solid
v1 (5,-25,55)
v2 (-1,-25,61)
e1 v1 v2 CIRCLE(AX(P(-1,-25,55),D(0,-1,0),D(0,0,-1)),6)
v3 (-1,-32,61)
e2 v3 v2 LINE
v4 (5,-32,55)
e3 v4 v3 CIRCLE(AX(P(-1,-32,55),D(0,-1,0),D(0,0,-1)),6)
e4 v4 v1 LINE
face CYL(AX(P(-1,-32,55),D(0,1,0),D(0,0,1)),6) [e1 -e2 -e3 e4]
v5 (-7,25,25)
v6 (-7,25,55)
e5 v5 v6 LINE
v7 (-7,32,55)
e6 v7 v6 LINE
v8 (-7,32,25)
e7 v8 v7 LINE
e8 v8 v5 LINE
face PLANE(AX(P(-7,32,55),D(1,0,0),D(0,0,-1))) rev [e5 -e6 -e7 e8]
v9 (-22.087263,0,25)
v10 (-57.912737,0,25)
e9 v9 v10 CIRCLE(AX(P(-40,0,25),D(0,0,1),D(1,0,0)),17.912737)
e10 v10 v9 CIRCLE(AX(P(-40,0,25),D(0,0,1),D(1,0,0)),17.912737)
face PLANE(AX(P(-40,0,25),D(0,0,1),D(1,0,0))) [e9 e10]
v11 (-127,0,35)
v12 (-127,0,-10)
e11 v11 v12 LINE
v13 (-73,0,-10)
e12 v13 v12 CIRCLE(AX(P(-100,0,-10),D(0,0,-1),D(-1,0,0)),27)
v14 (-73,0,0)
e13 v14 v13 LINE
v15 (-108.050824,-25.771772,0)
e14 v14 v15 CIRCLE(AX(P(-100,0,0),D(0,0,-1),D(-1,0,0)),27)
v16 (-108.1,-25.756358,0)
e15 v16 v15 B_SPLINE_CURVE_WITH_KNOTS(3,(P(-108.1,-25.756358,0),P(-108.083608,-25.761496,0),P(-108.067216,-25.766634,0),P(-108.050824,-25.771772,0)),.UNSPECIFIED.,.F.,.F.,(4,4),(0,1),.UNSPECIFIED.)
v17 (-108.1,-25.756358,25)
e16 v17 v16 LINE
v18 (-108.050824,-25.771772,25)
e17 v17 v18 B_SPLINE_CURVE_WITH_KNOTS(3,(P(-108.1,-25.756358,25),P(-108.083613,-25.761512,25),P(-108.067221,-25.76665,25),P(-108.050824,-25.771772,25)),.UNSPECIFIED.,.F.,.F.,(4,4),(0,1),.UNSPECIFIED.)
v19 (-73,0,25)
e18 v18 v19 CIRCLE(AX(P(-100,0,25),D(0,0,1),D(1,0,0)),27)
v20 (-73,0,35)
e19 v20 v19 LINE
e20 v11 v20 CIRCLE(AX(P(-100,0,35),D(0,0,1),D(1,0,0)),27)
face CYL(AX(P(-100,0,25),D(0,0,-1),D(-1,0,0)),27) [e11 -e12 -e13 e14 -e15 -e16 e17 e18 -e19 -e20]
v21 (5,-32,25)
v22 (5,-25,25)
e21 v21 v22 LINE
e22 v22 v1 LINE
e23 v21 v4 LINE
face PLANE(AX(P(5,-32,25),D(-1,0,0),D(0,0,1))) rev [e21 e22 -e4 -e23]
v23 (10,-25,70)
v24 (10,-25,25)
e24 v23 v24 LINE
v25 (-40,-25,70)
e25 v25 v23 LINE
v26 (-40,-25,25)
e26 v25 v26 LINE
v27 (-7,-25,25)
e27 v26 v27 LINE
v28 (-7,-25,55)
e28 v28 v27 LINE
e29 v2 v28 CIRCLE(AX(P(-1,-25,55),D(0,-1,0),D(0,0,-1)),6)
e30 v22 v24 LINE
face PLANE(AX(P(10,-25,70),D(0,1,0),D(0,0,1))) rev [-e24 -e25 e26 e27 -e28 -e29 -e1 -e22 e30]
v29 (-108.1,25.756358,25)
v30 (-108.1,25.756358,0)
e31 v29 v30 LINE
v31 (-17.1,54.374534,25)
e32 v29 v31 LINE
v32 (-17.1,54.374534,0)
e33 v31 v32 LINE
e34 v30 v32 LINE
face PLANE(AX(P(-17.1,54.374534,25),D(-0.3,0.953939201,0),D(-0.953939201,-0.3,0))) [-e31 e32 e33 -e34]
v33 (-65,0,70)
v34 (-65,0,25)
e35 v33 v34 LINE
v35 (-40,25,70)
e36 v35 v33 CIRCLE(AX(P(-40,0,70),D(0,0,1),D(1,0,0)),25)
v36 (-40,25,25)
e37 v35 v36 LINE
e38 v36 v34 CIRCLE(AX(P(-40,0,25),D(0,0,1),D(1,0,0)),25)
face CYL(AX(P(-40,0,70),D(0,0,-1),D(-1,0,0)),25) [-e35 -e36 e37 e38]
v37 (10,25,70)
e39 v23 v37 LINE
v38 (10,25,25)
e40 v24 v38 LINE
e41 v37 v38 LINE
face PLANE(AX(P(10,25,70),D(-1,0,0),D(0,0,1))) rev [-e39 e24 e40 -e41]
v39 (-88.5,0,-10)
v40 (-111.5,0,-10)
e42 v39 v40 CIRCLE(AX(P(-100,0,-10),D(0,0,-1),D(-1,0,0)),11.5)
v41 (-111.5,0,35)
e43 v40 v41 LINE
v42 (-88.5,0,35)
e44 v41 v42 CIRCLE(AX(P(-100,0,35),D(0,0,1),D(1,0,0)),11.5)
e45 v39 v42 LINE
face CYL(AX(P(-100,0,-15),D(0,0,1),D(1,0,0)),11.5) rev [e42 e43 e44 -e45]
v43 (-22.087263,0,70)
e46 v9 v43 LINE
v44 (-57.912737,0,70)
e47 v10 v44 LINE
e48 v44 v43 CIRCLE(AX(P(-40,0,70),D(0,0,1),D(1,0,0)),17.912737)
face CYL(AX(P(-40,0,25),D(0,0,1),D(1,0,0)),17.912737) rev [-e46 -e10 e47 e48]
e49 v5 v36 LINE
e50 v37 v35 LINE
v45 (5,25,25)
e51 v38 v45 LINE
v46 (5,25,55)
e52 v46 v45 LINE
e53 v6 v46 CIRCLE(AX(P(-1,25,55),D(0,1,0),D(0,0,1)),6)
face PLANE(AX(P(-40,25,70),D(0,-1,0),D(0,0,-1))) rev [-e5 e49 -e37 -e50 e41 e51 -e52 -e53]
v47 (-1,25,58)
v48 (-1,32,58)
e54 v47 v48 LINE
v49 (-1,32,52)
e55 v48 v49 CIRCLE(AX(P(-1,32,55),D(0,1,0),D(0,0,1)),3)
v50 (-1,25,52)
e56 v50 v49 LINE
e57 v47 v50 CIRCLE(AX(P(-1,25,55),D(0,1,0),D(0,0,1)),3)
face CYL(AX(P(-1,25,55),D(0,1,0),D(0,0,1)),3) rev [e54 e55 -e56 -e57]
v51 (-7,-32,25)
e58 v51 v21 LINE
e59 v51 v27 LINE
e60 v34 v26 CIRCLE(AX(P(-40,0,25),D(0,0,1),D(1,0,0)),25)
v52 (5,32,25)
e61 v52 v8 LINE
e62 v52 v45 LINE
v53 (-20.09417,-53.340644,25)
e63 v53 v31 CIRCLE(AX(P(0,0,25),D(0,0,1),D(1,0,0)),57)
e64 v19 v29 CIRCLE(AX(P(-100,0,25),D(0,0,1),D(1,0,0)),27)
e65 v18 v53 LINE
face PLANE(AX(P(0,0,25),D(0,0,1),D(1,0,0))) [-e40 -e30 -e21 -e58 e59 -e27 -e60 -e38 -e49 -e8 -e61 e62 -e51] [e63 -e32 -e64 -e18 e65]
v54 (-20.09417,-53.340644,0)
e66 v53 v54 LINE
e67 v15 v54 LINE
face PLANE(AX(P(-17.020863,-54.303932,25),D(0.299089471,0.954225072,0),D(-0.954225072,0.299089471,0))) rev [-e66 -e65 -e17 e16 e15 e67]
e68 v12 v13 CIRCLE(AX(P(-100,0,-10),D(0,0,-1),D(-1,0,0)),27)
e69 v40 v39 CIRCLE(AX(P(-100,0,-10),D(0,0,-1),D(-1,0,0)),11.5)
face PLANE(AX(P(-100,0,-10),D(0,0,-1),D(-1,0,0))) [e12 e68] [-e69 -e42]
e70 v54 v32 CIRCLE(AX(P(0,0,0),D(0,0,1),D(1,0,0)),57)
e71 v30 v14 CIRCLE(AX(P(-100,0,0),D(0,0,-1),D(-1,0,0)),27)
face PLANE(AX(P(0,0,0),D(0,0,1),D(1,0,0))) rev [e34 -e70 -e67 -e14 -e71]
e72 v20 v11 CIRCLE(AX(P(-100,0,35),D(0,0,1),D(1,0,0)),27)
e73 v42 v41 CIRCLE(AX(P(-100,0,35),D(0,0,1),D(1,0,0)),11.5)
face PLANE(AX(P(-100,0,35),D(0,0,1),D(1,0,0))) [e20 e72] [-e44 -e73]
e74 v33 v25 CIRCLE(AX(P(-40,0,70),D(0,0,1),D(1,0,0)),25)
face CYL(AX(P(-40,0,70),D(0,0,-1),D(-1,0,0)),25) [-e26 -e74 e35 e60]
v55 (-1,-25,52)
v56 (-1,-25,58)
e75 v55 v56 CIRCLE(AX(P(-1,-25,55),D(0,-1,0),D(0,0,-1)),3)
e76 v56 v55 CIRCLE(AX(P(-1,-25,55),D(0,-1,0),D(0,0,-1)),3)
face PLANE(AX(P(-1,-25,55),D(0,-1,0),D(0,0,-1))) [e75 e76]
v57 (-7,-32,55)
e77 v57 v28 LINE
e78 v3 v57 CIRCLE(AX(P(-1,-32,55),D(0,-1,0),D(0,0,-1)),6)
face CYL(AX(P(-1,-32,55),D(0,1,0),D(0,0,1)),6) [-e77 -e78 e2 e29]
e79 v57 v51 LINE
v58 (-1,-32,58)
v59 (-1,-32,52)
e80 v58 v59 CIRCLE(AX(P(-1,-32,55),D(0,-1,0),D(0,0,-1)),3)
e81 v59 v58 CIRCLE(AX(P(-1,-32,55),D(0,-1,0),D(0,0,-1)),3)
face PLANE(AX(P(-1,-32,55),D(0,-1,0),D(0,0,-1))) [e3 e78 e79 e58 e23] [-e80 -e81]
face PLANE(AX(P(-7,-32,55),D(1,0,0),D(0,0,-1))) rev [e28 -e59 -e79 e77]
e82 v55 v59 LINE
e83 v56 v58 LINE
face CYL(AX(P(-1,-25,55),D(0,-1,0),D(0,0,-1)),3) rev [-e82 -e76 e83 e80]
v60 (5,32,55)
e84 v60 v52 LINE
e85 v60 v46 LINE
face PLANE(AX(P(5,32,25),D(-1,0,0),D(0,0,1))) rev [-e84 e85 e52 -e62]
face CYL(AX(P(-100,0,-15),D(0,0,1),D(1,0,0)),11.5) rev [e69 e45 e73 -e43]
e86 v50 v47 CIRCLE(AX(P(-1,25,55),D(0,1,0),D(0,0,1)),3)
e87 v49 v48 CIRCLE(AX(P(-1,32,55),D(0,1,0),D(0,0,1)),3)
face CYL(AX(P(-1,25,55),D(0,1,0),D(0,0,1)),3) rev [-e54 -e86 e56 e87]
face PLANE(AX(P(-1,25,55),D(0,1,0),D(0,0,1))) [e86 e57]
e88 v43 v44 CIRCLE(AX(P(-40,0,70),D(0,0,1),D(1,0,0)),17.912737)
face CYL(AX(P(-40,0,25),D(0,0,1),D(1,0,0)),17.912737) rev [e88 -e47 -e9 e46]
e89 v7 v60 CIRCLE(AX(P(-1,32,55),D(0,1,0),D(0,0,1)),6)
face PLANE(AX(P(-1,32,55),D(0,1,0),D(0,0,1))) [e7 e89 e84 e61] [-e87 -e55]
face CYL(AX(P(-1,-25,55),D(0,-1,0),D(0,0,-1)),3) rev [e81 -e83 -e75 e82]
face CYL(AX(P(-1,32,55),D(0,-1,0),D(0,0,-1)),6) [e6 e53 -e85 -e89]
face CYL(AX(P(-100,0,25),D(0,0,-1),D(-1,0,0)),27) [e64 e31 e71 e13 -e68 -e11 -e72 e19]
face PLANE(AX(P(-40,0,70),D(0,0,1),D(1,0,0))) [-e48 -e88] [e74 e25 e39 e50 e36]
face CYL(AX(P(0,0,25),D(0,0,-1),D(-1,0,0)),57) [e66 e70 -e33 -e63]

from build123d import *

# Parameters (mm, degrees)
BASE_PLATE_DEPTH      = 25
FRONT_HUB_SKETCH_R    = 27
FRONT_HUB_54_DEPTH    = 10
REAR_START            = 10
REAR_HUB_SKETCH_R     = 27
REAR_HUB_54_DEPTH     = 10
HUB_BORE_SKETCH_R     = 11.5
HUB_BORE_23_DEPTH     = 50
BEARING_BLOCK_DEPTH   = 45
BLOCK_BORE_SKETCH_R   = 17.912737299
BLOCK_BORE_35_8_DEPTH = 45
LUG_TAB_1_DEPTH       = 7
LUG_START             = 7
LUG_TAB_2_DEPTH       = 7
LUG_HOLE_1_SKETCH_R   = 3
LUG_HOLE_1_6_DEPTH    = 7
LUG_START_2           = -7
LUG_HOLE_2_SKETCH_R   = 3
LUG_HOLE_2_6_DEPTH    = 7


with BuildPart() as part:
    # Base Plate Sketch → Base Plate (new body)
    with BuildSketch(Plane.XY):
        with BuildLine():
            Line((-17.1, 54.374534481), (-108.1, 25.756358438))
            ThreePointArc((-108.1, 25.756358438), (-127, 0), (-108.1, -25.756358438))
            Line((-108.1, -25.756358438), (-108.05082408, -25.771771993))
            Line((-108.05082408, -25.771771993), (-20.094170087, -53.340644245))
            ThreePointArc((-20.094170087, -53.340644245), (56.977991401, -1.583823185), (-17.1, 54.374534481))
        make_face()
    extrude(amount=BASE_PLATE_DEPTH)

    # Front Hub Sketch → Front Hub _54 (add)
    with BuildSketch(Plane.XY.offset(25)):
        with Locations(Location((-100, 0, 0), (0, 0, 252.542396876))):
            Circle(FRONT_HUB_SKETCH_R)
    extrude(amount=FRONT_HUB_54_DEPTH)

    # Rear Hub Sketch → Rear Hub _54 (add)
    with BuildSketch(Plane(origin=(0, 0, 0), x_dir=(-1, 0, 0), z_dir=(0, 0, -1)).offset(REAR_START)):
        with Locations((100, 0)):
            Circle(REAR_HUB_SKETCH_R)
    extrude(amount=-REAR_HUB_54_DEPTH)

    # Hub Bore Sketch → Hub Bore _23 (cut)
    with BuildSketch(Plane.XY.offset(35)):
        with Locations((-100, 0)):
            Circle(HUB_BORE_SKETCH_R)
    extrude(amount=-HUB_BORE_23_DEPTH, mode=Mode.SUBTRACT)

    # Bearing Block Sketch → Bearing Block (add)
    with BuildSketch(Plane.XY.offset(25)):
        with BuildLine():
            Line((-40, 25), (10, 25))
            Line((10, 25), (10, -25))
            Line((10, -25), (-40, -25))
            ThreePointArc((-40, -25), (-65, 0), (-40, 25))
        make_face()
    extrude(amount=BEARING_BLOCK_DEPTH)

    # Block Bore Sketch → Block Bore _35.8 (cut)
    with BuildSketch(Plane.XY.offset(70)):
        with Locations((-40, 0)):
            Circle(BLOCK_BORE_SKETCH_R)
    extrude(amount=-BLOCK_BORE_35_8_DEPTH, mode=Mode.SUBTRACT)

    # Lug Tab 1 Sketch → Lug Tab 1 (add)
    with BuildSketch(Plane.XZ.offset(25)):
        with BuildLine():
            Line((5, 25), (5, 55))
            ThreePointArc((5, 55), (-1, 61), (-7, 55))
            Line((-7, 55), (-7, 25))
            Line((-7, 25), (5, 25))
        make_face()
    extrude(amount=LUG_TAB_1_DEPTH)

    # Lug Tab 2 Sketch → Lug Tab 2 (add)
    with BuildSketch(Plane(origin=(0, 25, 0), x_dir=(1, 0, 0), z_dir=(0, 1, 0)).offset(LUG_START)):
        with BuildLine():
            Line((5, -25), (5, -55))
            ThreePointArc((5, -55), (-1, -61), (-7, -55))
            Line((-7, -55), (-7, -25))
            Line((-7, -25), (5, -25))
        make_face()
    extrude(amount=-LUG_TAB_2_DEPTH)

    # Lug Hole 1 Sketch → Lug Hole 1 _6 (cut)
    with BuildSketch(Plane.XZ.offset(32)):
        with Locations(Location((-1, 55, 0), (0, 0, 270))):
            Circle(LUG_HOLE_1_SKETCH_R)
    extrude(amount=-LUG_HOLE_1_6_DEPTH, mode=Mode.SUBTRACT)

    # Lug Hole 2 Sketch → Lug Hole 2 _6 (cut)
    with BuildSketch(Plane(origin=(0, 32, 0), x_dir=(1, 0, 0), z_dir=(0, 1, 0)).offset(LUG_START_2)):
        with Locations(Location((-1, -55, 0), (0, 0, 90))):
            Circle(LUG_HOLE_2_SKETCH_R)
    extrude(amount=LUG_HOLE_2_6_DEPTH, mode=Mode.SUBTRACT)


solid = part.part
